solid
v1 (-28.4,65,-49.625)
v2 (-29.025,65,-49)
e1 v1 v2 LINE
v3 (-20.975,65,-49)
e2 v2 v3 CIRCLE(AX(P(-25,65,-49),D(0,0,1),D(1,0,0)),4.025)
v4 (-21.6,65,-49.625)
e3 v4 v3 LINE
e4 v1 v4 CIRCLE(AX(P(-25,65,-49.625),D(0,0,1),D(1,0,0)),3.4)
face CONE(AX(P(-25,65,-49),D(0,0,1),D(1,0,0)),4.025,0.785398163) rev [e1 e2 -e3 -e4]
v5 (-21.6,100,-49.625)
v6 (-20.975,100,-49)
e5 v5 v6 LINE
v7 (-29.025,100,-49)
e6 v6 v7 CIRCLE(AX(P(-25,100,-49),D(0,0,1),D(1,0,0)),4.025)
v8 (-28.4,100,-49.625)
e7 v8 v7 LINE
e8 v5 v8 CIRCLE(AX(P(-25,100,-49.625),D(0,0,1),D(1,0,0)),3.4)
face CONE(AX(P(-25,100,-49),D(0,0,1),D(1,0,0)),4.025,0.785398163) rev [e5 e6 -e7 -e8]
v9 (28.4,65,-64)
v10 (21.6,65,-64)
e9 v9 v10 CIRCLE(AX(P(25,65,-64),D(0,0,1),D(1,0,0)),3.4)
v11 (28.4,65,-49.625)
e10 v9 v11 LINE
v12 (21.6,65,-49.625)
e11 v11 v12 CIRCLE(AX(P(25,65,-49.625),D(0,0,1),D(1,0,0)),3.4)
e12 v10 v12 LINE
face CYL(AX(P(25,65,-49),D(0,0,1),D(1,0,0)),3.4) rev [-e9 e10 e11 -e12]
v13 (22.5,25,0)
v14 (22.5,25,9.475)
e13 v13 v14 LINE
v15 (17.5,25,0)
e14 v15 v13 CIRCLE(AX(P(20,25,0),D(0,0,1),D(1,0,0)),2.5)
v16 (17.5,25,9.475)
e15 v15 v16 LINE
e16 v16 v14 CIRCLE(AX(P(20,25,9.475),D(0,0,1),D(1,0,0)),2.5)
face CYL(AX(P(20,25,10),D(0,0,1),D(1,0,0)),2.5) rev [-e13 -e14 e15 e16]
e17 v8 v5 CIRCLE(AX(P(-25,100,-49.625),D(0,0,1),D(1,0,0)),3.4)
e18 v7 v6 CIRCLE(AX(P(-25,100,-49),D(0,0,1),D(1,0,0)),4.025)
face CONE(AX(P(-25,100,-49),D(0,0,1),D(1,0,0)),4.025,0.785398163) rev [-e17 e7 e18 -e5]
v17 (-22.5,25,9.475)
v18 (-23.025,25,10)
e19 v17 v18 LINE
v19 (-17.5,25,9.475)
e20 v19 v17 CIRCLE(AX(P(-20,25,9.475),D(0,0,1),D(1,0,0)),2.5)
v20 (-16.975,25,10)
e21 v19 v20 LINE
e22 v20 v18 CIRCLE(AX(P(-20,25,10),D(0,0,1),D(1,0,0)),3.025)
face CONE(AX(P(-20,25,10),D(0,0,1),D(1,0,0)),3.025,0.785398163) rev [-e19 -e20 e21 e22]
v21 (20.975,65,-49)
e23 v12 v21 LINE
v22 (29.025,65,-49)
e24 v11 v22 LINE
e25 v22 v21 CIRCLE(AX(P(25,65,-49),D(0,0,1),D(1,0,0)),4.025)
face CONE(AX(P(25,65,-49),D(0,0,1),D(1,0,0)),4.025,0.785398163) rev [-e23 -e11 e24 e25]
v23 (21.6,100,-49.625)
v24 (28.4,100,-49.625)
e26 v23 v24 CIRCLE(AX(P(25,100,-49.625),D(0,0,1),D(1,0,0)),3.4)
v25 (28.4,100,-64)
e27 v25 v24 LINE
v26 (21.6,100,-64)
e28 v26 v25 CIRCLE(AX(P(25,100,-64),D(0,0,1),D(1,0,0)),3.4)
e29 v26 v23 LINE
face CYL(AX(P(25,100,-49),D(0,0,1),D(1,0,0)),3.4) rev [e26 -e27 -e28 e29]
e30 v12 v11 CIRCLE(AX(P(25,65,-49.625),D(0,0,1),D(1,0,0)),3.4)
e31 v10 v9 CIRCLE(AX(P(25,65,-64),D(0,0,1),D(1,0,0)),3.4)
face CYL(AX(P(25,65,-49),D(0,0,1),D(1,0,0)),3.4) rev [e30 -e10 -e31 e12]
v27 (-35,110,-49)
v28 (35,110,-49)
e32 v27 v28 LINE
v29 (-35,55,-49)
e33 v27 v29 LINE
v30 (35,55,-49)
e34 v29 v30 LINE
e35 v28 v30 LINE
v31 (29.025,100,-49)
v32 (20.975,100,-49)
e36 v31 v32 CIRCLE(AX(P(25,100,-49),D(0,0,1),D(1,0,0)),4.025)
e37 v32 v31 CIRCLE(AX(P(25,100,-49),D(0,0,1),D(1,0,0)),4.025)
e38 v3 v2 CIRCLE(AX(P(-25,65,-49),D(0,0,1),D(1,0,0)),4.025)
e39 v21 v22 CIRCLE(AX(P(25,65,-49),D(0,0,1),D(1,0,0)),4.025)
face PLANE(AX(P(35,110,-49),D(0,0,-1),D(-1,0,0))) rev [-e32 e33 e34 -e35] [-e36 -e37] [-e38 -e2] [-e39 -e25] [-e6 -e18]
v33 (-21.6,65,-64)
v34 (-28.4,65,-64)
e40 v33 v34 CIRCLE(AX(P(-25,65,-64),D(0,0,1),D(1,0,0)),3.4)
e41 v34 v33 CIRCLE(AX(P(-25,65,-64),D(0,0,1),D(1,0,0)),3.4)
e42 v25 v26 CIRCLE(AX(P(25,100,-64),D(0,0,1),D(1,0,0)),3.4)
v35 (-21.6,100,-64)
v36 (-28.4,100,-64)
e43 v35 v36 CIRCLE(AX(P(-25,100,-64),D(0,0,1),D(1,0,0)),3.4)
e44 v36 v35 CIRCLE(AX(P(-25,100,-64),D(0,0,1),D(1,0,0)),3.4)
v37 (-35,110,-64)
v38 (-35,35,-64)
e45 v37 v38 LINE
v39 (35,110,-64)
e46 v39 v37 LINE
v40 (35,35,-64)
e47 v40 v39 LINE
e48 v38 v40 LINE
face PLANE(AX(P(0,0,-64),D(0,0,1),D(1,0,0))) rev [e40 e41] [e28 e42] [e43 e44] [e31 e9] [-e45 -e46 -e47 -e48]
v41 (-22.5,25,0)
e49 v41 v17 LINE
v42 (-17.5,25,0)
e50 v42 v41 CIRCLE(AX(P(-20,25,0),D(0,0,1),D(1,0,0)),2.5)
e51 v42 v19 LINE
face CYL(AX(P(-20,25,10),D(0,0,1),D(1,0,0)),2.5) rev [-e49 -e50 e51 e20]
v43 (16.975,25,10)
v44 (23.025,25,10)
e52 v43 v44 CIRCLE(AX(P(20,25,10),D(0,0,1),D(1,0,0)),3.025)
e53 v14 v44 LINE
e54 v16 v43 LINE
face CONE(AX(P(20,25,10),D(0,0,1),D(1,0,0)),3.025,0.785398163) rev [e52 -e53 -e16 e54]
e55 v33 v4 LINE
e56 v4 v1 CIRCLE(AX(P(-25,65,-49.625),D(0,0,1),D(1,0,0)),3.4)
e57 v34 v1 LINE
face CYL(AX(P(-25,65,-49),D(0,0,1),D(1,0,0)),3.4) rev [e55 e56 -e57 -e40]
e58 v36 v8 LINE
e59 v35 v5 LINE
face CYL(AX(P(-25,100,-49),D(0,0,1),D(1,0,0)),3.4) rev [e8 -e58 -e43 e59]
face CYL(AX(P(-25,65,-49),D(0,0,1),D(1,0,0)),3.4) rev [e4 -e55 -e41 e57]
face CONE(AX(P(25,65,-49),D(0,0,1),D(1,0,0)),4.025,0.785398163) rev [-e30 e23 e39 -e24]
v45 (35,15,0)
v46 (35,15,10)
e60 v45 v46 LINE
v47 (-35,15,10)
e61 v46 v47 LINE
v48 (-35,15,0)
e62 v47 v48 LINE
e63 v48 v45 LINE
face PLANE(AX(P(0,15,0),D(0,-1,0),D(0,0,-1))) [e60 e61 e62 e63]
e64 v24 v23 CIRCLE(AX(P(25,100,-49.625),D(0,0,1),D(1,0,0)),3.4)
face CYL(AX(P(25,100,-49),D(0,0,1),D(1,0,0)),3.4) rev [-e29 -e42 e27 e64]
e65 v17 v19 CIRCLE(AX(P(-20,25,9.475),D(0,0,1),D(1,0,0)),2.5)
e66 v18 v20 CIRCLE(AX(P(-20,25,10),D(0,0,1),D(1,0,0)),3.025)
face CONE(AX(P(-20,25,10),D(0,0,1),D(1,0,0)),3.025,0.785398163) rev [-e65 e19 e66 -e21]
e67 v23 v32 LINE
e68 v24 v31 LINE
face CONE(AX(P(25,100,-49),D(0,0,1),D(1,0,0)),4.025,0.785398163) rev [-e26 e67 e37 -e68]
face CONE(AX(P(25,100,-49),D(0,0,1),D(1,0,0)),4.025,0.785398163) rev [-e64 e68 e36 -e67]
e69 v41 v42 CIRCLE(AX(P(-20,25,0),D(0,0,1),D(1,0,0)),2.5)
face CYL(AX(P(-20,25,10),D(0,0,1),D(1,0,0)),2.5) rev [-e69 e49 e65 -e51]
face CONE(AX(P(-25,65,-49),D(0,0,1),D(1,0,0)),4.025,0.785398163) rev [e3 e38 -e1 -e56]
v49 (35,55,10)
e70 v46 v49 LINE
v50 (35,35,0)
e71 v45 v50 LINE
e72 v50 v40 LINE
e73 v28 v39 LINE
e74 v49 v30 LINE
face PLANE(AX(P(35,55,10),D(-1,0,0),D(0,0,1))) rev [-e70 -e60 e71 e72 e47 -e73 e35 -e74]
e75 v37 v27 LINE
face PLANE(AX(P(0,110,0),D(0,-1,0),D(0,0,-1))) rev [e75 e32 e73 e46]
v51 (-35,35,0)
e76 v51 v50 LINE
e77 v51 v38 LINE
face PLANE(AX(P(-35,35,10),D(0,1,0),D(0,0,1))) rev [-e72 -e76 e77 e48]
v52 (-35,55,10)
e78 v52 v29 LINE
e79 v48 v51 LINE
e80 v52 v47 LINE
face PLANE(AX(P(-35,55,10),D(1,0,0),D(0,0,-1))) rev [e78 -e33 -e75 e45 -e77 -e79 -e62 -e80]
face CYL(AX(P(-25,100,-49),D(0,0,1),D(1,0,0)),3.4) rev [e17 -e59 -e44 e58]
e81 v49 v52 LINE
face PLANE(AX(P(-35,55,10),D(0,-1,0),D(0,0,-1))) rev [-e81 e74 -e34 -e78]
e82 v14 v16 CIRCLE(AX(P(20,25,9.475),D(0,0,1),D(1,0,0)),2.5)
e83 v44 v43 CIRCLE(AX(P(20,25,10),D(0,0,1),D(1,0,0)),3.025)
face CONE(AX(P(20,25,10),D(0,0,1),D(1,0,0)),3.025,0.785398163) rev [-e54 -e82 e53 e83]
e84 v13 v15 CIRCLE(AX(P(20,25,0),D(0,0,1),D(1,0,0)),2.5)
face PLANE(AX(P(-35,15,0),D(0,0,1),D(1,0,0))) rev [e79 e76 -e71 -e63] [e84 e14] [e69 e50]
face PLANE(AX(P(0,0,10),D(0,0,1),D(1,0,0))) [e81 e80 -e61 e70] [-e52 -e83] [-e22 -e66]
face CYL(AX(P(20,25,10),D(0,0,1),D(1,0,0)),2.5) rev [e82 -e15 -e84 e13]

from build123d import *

# Parameters (mm, degrees)
EXTRUDE_1_DEPTH              = 10
EXTRUDE_1_DEPTH_BACK         = 64
SKETCH_1_W                   = 70
SKETCH_1_H                   = 20
SKETCH_2_W                   = 70
SKETCH_2_H                   = 10
EXTRUDE_2_DEPTH              = 20
SKETCH_3_W                   = 70
SKETCH_3_H                   = 15
EXTRUDE_3_DEPTH              = 55
HOLE_WIZARD_M8_1_D           = 6.8
HOLE_WIZARD_M8_1_DEPTH       = 17.707073895
HOLE_WIZARD_M8_1_CSINK_D     = 8.05
HOLE_WIZARD_M8_1_CSINK_ANGLE = 90
HOLE_WIZARD_M8_1_TIP         = 2.042926105
HOLE_WIZARD_M6_1_D           = 5
HOLE_WIZARD_M6_1_DEPTH       = 13.497848452
HOLE_WIZARD_M6_1_CSINK_D     = 6.05
HOLE_WIZARD_M6_1_CSINK_ANGLE = 90
HOLE_WIZARD_M6_1_TIP         = 1.502151548


with BuildPart() as part:
    # 草图1 → 凸台-拉伸1 (new, two sides: drawn at the far end of the back side and taken through both)
    with BuildSketch(Plane.XY.offset(-EXTRUDE_1_DEPTH_BACK)):
        with Locations((0, 45)):
            Rectangle(SKETCH_1_W, SKETCH_1_H)
    extrude(amount=EXTRUDE_1_DEPTH + EXTRUDE_1_DEPTH_BACK)

    # 草图2 → 凸台-拉伸2 (add)
    with BuildSketch(Plane.XZ.offset(-35)):
        with Locations((0, 5)):
            Rectangle(SKETCH_2_W, SKETCH_2_H)
    extrude(amount=EXTRUDE_2_DEPTH)

    # 草图3 → 凸台-拉伸3 (add)
    with BuildSketch(Plane(origin=(0, 55, 0), x_dir=(1, 0, 0), z_dir=(0, 1, 0))):
        with Locations((0, 56.5)):
            Rectangle(SKETCH_3_W, SKETCH_3_H)
    extrude(amount=EXTRUDE_3_DEPTH)

    # M8 螺纹孔1
    with Locations(Plane.XY.offset(-49)):
        with Locations((25, 100), (25, 65), (-25, 65), (-25, 100)):
            CounterSinkHole(HOLE_WIZARD_M8_1_D / 2, HOLE_WIZARD_M8_1_CSINK_D / 2, depth=HOLE_WIZARD_M8_1_DEPTH, counter_sink_angle=HOLE_WIZARD_M8_1_CSINK_ANGLE)
            with Locations((0, 0, -(HOLE_WIZARD_M8_1_DEPTH + HOLE_WIZARD_M8_1_TIP / 2))):  # 118° drill point
                Cone(0, HOLE_WIZARD_M8_1_D / 2, HOLE_WIZARD_M8_1_TIP, mode=Mode.SUBTRACT)

    # M6 螺纹孔1
    with Locations(Plane.XY.offset(10)):
        with Locations((20, 25), (-20, 25)):
            CounterSinkHole(HOLE_WIZARD_M6_1_D / 2, HOLE_WIZARD_M6_1_CSINK_D / 2, depth=HOLE_WIZARD_M6_1_DEPTH, counter_sink_angle=HOLE_WIZARD_M6_1_CSINK_ANGLE)
            with Locations((0, 0, -(HOLE_WIZARD_M6_1_DEPTH + HOLE_WIZARD_M6_1_TIP / 2))):  # 118° drill point
                Cone(0, HOLE_WIZARD_M6_1_D / 2, HOLE_WIZARD_M6_1_TIP, mode=Mode.SUBTRACT)


solid = part.part
